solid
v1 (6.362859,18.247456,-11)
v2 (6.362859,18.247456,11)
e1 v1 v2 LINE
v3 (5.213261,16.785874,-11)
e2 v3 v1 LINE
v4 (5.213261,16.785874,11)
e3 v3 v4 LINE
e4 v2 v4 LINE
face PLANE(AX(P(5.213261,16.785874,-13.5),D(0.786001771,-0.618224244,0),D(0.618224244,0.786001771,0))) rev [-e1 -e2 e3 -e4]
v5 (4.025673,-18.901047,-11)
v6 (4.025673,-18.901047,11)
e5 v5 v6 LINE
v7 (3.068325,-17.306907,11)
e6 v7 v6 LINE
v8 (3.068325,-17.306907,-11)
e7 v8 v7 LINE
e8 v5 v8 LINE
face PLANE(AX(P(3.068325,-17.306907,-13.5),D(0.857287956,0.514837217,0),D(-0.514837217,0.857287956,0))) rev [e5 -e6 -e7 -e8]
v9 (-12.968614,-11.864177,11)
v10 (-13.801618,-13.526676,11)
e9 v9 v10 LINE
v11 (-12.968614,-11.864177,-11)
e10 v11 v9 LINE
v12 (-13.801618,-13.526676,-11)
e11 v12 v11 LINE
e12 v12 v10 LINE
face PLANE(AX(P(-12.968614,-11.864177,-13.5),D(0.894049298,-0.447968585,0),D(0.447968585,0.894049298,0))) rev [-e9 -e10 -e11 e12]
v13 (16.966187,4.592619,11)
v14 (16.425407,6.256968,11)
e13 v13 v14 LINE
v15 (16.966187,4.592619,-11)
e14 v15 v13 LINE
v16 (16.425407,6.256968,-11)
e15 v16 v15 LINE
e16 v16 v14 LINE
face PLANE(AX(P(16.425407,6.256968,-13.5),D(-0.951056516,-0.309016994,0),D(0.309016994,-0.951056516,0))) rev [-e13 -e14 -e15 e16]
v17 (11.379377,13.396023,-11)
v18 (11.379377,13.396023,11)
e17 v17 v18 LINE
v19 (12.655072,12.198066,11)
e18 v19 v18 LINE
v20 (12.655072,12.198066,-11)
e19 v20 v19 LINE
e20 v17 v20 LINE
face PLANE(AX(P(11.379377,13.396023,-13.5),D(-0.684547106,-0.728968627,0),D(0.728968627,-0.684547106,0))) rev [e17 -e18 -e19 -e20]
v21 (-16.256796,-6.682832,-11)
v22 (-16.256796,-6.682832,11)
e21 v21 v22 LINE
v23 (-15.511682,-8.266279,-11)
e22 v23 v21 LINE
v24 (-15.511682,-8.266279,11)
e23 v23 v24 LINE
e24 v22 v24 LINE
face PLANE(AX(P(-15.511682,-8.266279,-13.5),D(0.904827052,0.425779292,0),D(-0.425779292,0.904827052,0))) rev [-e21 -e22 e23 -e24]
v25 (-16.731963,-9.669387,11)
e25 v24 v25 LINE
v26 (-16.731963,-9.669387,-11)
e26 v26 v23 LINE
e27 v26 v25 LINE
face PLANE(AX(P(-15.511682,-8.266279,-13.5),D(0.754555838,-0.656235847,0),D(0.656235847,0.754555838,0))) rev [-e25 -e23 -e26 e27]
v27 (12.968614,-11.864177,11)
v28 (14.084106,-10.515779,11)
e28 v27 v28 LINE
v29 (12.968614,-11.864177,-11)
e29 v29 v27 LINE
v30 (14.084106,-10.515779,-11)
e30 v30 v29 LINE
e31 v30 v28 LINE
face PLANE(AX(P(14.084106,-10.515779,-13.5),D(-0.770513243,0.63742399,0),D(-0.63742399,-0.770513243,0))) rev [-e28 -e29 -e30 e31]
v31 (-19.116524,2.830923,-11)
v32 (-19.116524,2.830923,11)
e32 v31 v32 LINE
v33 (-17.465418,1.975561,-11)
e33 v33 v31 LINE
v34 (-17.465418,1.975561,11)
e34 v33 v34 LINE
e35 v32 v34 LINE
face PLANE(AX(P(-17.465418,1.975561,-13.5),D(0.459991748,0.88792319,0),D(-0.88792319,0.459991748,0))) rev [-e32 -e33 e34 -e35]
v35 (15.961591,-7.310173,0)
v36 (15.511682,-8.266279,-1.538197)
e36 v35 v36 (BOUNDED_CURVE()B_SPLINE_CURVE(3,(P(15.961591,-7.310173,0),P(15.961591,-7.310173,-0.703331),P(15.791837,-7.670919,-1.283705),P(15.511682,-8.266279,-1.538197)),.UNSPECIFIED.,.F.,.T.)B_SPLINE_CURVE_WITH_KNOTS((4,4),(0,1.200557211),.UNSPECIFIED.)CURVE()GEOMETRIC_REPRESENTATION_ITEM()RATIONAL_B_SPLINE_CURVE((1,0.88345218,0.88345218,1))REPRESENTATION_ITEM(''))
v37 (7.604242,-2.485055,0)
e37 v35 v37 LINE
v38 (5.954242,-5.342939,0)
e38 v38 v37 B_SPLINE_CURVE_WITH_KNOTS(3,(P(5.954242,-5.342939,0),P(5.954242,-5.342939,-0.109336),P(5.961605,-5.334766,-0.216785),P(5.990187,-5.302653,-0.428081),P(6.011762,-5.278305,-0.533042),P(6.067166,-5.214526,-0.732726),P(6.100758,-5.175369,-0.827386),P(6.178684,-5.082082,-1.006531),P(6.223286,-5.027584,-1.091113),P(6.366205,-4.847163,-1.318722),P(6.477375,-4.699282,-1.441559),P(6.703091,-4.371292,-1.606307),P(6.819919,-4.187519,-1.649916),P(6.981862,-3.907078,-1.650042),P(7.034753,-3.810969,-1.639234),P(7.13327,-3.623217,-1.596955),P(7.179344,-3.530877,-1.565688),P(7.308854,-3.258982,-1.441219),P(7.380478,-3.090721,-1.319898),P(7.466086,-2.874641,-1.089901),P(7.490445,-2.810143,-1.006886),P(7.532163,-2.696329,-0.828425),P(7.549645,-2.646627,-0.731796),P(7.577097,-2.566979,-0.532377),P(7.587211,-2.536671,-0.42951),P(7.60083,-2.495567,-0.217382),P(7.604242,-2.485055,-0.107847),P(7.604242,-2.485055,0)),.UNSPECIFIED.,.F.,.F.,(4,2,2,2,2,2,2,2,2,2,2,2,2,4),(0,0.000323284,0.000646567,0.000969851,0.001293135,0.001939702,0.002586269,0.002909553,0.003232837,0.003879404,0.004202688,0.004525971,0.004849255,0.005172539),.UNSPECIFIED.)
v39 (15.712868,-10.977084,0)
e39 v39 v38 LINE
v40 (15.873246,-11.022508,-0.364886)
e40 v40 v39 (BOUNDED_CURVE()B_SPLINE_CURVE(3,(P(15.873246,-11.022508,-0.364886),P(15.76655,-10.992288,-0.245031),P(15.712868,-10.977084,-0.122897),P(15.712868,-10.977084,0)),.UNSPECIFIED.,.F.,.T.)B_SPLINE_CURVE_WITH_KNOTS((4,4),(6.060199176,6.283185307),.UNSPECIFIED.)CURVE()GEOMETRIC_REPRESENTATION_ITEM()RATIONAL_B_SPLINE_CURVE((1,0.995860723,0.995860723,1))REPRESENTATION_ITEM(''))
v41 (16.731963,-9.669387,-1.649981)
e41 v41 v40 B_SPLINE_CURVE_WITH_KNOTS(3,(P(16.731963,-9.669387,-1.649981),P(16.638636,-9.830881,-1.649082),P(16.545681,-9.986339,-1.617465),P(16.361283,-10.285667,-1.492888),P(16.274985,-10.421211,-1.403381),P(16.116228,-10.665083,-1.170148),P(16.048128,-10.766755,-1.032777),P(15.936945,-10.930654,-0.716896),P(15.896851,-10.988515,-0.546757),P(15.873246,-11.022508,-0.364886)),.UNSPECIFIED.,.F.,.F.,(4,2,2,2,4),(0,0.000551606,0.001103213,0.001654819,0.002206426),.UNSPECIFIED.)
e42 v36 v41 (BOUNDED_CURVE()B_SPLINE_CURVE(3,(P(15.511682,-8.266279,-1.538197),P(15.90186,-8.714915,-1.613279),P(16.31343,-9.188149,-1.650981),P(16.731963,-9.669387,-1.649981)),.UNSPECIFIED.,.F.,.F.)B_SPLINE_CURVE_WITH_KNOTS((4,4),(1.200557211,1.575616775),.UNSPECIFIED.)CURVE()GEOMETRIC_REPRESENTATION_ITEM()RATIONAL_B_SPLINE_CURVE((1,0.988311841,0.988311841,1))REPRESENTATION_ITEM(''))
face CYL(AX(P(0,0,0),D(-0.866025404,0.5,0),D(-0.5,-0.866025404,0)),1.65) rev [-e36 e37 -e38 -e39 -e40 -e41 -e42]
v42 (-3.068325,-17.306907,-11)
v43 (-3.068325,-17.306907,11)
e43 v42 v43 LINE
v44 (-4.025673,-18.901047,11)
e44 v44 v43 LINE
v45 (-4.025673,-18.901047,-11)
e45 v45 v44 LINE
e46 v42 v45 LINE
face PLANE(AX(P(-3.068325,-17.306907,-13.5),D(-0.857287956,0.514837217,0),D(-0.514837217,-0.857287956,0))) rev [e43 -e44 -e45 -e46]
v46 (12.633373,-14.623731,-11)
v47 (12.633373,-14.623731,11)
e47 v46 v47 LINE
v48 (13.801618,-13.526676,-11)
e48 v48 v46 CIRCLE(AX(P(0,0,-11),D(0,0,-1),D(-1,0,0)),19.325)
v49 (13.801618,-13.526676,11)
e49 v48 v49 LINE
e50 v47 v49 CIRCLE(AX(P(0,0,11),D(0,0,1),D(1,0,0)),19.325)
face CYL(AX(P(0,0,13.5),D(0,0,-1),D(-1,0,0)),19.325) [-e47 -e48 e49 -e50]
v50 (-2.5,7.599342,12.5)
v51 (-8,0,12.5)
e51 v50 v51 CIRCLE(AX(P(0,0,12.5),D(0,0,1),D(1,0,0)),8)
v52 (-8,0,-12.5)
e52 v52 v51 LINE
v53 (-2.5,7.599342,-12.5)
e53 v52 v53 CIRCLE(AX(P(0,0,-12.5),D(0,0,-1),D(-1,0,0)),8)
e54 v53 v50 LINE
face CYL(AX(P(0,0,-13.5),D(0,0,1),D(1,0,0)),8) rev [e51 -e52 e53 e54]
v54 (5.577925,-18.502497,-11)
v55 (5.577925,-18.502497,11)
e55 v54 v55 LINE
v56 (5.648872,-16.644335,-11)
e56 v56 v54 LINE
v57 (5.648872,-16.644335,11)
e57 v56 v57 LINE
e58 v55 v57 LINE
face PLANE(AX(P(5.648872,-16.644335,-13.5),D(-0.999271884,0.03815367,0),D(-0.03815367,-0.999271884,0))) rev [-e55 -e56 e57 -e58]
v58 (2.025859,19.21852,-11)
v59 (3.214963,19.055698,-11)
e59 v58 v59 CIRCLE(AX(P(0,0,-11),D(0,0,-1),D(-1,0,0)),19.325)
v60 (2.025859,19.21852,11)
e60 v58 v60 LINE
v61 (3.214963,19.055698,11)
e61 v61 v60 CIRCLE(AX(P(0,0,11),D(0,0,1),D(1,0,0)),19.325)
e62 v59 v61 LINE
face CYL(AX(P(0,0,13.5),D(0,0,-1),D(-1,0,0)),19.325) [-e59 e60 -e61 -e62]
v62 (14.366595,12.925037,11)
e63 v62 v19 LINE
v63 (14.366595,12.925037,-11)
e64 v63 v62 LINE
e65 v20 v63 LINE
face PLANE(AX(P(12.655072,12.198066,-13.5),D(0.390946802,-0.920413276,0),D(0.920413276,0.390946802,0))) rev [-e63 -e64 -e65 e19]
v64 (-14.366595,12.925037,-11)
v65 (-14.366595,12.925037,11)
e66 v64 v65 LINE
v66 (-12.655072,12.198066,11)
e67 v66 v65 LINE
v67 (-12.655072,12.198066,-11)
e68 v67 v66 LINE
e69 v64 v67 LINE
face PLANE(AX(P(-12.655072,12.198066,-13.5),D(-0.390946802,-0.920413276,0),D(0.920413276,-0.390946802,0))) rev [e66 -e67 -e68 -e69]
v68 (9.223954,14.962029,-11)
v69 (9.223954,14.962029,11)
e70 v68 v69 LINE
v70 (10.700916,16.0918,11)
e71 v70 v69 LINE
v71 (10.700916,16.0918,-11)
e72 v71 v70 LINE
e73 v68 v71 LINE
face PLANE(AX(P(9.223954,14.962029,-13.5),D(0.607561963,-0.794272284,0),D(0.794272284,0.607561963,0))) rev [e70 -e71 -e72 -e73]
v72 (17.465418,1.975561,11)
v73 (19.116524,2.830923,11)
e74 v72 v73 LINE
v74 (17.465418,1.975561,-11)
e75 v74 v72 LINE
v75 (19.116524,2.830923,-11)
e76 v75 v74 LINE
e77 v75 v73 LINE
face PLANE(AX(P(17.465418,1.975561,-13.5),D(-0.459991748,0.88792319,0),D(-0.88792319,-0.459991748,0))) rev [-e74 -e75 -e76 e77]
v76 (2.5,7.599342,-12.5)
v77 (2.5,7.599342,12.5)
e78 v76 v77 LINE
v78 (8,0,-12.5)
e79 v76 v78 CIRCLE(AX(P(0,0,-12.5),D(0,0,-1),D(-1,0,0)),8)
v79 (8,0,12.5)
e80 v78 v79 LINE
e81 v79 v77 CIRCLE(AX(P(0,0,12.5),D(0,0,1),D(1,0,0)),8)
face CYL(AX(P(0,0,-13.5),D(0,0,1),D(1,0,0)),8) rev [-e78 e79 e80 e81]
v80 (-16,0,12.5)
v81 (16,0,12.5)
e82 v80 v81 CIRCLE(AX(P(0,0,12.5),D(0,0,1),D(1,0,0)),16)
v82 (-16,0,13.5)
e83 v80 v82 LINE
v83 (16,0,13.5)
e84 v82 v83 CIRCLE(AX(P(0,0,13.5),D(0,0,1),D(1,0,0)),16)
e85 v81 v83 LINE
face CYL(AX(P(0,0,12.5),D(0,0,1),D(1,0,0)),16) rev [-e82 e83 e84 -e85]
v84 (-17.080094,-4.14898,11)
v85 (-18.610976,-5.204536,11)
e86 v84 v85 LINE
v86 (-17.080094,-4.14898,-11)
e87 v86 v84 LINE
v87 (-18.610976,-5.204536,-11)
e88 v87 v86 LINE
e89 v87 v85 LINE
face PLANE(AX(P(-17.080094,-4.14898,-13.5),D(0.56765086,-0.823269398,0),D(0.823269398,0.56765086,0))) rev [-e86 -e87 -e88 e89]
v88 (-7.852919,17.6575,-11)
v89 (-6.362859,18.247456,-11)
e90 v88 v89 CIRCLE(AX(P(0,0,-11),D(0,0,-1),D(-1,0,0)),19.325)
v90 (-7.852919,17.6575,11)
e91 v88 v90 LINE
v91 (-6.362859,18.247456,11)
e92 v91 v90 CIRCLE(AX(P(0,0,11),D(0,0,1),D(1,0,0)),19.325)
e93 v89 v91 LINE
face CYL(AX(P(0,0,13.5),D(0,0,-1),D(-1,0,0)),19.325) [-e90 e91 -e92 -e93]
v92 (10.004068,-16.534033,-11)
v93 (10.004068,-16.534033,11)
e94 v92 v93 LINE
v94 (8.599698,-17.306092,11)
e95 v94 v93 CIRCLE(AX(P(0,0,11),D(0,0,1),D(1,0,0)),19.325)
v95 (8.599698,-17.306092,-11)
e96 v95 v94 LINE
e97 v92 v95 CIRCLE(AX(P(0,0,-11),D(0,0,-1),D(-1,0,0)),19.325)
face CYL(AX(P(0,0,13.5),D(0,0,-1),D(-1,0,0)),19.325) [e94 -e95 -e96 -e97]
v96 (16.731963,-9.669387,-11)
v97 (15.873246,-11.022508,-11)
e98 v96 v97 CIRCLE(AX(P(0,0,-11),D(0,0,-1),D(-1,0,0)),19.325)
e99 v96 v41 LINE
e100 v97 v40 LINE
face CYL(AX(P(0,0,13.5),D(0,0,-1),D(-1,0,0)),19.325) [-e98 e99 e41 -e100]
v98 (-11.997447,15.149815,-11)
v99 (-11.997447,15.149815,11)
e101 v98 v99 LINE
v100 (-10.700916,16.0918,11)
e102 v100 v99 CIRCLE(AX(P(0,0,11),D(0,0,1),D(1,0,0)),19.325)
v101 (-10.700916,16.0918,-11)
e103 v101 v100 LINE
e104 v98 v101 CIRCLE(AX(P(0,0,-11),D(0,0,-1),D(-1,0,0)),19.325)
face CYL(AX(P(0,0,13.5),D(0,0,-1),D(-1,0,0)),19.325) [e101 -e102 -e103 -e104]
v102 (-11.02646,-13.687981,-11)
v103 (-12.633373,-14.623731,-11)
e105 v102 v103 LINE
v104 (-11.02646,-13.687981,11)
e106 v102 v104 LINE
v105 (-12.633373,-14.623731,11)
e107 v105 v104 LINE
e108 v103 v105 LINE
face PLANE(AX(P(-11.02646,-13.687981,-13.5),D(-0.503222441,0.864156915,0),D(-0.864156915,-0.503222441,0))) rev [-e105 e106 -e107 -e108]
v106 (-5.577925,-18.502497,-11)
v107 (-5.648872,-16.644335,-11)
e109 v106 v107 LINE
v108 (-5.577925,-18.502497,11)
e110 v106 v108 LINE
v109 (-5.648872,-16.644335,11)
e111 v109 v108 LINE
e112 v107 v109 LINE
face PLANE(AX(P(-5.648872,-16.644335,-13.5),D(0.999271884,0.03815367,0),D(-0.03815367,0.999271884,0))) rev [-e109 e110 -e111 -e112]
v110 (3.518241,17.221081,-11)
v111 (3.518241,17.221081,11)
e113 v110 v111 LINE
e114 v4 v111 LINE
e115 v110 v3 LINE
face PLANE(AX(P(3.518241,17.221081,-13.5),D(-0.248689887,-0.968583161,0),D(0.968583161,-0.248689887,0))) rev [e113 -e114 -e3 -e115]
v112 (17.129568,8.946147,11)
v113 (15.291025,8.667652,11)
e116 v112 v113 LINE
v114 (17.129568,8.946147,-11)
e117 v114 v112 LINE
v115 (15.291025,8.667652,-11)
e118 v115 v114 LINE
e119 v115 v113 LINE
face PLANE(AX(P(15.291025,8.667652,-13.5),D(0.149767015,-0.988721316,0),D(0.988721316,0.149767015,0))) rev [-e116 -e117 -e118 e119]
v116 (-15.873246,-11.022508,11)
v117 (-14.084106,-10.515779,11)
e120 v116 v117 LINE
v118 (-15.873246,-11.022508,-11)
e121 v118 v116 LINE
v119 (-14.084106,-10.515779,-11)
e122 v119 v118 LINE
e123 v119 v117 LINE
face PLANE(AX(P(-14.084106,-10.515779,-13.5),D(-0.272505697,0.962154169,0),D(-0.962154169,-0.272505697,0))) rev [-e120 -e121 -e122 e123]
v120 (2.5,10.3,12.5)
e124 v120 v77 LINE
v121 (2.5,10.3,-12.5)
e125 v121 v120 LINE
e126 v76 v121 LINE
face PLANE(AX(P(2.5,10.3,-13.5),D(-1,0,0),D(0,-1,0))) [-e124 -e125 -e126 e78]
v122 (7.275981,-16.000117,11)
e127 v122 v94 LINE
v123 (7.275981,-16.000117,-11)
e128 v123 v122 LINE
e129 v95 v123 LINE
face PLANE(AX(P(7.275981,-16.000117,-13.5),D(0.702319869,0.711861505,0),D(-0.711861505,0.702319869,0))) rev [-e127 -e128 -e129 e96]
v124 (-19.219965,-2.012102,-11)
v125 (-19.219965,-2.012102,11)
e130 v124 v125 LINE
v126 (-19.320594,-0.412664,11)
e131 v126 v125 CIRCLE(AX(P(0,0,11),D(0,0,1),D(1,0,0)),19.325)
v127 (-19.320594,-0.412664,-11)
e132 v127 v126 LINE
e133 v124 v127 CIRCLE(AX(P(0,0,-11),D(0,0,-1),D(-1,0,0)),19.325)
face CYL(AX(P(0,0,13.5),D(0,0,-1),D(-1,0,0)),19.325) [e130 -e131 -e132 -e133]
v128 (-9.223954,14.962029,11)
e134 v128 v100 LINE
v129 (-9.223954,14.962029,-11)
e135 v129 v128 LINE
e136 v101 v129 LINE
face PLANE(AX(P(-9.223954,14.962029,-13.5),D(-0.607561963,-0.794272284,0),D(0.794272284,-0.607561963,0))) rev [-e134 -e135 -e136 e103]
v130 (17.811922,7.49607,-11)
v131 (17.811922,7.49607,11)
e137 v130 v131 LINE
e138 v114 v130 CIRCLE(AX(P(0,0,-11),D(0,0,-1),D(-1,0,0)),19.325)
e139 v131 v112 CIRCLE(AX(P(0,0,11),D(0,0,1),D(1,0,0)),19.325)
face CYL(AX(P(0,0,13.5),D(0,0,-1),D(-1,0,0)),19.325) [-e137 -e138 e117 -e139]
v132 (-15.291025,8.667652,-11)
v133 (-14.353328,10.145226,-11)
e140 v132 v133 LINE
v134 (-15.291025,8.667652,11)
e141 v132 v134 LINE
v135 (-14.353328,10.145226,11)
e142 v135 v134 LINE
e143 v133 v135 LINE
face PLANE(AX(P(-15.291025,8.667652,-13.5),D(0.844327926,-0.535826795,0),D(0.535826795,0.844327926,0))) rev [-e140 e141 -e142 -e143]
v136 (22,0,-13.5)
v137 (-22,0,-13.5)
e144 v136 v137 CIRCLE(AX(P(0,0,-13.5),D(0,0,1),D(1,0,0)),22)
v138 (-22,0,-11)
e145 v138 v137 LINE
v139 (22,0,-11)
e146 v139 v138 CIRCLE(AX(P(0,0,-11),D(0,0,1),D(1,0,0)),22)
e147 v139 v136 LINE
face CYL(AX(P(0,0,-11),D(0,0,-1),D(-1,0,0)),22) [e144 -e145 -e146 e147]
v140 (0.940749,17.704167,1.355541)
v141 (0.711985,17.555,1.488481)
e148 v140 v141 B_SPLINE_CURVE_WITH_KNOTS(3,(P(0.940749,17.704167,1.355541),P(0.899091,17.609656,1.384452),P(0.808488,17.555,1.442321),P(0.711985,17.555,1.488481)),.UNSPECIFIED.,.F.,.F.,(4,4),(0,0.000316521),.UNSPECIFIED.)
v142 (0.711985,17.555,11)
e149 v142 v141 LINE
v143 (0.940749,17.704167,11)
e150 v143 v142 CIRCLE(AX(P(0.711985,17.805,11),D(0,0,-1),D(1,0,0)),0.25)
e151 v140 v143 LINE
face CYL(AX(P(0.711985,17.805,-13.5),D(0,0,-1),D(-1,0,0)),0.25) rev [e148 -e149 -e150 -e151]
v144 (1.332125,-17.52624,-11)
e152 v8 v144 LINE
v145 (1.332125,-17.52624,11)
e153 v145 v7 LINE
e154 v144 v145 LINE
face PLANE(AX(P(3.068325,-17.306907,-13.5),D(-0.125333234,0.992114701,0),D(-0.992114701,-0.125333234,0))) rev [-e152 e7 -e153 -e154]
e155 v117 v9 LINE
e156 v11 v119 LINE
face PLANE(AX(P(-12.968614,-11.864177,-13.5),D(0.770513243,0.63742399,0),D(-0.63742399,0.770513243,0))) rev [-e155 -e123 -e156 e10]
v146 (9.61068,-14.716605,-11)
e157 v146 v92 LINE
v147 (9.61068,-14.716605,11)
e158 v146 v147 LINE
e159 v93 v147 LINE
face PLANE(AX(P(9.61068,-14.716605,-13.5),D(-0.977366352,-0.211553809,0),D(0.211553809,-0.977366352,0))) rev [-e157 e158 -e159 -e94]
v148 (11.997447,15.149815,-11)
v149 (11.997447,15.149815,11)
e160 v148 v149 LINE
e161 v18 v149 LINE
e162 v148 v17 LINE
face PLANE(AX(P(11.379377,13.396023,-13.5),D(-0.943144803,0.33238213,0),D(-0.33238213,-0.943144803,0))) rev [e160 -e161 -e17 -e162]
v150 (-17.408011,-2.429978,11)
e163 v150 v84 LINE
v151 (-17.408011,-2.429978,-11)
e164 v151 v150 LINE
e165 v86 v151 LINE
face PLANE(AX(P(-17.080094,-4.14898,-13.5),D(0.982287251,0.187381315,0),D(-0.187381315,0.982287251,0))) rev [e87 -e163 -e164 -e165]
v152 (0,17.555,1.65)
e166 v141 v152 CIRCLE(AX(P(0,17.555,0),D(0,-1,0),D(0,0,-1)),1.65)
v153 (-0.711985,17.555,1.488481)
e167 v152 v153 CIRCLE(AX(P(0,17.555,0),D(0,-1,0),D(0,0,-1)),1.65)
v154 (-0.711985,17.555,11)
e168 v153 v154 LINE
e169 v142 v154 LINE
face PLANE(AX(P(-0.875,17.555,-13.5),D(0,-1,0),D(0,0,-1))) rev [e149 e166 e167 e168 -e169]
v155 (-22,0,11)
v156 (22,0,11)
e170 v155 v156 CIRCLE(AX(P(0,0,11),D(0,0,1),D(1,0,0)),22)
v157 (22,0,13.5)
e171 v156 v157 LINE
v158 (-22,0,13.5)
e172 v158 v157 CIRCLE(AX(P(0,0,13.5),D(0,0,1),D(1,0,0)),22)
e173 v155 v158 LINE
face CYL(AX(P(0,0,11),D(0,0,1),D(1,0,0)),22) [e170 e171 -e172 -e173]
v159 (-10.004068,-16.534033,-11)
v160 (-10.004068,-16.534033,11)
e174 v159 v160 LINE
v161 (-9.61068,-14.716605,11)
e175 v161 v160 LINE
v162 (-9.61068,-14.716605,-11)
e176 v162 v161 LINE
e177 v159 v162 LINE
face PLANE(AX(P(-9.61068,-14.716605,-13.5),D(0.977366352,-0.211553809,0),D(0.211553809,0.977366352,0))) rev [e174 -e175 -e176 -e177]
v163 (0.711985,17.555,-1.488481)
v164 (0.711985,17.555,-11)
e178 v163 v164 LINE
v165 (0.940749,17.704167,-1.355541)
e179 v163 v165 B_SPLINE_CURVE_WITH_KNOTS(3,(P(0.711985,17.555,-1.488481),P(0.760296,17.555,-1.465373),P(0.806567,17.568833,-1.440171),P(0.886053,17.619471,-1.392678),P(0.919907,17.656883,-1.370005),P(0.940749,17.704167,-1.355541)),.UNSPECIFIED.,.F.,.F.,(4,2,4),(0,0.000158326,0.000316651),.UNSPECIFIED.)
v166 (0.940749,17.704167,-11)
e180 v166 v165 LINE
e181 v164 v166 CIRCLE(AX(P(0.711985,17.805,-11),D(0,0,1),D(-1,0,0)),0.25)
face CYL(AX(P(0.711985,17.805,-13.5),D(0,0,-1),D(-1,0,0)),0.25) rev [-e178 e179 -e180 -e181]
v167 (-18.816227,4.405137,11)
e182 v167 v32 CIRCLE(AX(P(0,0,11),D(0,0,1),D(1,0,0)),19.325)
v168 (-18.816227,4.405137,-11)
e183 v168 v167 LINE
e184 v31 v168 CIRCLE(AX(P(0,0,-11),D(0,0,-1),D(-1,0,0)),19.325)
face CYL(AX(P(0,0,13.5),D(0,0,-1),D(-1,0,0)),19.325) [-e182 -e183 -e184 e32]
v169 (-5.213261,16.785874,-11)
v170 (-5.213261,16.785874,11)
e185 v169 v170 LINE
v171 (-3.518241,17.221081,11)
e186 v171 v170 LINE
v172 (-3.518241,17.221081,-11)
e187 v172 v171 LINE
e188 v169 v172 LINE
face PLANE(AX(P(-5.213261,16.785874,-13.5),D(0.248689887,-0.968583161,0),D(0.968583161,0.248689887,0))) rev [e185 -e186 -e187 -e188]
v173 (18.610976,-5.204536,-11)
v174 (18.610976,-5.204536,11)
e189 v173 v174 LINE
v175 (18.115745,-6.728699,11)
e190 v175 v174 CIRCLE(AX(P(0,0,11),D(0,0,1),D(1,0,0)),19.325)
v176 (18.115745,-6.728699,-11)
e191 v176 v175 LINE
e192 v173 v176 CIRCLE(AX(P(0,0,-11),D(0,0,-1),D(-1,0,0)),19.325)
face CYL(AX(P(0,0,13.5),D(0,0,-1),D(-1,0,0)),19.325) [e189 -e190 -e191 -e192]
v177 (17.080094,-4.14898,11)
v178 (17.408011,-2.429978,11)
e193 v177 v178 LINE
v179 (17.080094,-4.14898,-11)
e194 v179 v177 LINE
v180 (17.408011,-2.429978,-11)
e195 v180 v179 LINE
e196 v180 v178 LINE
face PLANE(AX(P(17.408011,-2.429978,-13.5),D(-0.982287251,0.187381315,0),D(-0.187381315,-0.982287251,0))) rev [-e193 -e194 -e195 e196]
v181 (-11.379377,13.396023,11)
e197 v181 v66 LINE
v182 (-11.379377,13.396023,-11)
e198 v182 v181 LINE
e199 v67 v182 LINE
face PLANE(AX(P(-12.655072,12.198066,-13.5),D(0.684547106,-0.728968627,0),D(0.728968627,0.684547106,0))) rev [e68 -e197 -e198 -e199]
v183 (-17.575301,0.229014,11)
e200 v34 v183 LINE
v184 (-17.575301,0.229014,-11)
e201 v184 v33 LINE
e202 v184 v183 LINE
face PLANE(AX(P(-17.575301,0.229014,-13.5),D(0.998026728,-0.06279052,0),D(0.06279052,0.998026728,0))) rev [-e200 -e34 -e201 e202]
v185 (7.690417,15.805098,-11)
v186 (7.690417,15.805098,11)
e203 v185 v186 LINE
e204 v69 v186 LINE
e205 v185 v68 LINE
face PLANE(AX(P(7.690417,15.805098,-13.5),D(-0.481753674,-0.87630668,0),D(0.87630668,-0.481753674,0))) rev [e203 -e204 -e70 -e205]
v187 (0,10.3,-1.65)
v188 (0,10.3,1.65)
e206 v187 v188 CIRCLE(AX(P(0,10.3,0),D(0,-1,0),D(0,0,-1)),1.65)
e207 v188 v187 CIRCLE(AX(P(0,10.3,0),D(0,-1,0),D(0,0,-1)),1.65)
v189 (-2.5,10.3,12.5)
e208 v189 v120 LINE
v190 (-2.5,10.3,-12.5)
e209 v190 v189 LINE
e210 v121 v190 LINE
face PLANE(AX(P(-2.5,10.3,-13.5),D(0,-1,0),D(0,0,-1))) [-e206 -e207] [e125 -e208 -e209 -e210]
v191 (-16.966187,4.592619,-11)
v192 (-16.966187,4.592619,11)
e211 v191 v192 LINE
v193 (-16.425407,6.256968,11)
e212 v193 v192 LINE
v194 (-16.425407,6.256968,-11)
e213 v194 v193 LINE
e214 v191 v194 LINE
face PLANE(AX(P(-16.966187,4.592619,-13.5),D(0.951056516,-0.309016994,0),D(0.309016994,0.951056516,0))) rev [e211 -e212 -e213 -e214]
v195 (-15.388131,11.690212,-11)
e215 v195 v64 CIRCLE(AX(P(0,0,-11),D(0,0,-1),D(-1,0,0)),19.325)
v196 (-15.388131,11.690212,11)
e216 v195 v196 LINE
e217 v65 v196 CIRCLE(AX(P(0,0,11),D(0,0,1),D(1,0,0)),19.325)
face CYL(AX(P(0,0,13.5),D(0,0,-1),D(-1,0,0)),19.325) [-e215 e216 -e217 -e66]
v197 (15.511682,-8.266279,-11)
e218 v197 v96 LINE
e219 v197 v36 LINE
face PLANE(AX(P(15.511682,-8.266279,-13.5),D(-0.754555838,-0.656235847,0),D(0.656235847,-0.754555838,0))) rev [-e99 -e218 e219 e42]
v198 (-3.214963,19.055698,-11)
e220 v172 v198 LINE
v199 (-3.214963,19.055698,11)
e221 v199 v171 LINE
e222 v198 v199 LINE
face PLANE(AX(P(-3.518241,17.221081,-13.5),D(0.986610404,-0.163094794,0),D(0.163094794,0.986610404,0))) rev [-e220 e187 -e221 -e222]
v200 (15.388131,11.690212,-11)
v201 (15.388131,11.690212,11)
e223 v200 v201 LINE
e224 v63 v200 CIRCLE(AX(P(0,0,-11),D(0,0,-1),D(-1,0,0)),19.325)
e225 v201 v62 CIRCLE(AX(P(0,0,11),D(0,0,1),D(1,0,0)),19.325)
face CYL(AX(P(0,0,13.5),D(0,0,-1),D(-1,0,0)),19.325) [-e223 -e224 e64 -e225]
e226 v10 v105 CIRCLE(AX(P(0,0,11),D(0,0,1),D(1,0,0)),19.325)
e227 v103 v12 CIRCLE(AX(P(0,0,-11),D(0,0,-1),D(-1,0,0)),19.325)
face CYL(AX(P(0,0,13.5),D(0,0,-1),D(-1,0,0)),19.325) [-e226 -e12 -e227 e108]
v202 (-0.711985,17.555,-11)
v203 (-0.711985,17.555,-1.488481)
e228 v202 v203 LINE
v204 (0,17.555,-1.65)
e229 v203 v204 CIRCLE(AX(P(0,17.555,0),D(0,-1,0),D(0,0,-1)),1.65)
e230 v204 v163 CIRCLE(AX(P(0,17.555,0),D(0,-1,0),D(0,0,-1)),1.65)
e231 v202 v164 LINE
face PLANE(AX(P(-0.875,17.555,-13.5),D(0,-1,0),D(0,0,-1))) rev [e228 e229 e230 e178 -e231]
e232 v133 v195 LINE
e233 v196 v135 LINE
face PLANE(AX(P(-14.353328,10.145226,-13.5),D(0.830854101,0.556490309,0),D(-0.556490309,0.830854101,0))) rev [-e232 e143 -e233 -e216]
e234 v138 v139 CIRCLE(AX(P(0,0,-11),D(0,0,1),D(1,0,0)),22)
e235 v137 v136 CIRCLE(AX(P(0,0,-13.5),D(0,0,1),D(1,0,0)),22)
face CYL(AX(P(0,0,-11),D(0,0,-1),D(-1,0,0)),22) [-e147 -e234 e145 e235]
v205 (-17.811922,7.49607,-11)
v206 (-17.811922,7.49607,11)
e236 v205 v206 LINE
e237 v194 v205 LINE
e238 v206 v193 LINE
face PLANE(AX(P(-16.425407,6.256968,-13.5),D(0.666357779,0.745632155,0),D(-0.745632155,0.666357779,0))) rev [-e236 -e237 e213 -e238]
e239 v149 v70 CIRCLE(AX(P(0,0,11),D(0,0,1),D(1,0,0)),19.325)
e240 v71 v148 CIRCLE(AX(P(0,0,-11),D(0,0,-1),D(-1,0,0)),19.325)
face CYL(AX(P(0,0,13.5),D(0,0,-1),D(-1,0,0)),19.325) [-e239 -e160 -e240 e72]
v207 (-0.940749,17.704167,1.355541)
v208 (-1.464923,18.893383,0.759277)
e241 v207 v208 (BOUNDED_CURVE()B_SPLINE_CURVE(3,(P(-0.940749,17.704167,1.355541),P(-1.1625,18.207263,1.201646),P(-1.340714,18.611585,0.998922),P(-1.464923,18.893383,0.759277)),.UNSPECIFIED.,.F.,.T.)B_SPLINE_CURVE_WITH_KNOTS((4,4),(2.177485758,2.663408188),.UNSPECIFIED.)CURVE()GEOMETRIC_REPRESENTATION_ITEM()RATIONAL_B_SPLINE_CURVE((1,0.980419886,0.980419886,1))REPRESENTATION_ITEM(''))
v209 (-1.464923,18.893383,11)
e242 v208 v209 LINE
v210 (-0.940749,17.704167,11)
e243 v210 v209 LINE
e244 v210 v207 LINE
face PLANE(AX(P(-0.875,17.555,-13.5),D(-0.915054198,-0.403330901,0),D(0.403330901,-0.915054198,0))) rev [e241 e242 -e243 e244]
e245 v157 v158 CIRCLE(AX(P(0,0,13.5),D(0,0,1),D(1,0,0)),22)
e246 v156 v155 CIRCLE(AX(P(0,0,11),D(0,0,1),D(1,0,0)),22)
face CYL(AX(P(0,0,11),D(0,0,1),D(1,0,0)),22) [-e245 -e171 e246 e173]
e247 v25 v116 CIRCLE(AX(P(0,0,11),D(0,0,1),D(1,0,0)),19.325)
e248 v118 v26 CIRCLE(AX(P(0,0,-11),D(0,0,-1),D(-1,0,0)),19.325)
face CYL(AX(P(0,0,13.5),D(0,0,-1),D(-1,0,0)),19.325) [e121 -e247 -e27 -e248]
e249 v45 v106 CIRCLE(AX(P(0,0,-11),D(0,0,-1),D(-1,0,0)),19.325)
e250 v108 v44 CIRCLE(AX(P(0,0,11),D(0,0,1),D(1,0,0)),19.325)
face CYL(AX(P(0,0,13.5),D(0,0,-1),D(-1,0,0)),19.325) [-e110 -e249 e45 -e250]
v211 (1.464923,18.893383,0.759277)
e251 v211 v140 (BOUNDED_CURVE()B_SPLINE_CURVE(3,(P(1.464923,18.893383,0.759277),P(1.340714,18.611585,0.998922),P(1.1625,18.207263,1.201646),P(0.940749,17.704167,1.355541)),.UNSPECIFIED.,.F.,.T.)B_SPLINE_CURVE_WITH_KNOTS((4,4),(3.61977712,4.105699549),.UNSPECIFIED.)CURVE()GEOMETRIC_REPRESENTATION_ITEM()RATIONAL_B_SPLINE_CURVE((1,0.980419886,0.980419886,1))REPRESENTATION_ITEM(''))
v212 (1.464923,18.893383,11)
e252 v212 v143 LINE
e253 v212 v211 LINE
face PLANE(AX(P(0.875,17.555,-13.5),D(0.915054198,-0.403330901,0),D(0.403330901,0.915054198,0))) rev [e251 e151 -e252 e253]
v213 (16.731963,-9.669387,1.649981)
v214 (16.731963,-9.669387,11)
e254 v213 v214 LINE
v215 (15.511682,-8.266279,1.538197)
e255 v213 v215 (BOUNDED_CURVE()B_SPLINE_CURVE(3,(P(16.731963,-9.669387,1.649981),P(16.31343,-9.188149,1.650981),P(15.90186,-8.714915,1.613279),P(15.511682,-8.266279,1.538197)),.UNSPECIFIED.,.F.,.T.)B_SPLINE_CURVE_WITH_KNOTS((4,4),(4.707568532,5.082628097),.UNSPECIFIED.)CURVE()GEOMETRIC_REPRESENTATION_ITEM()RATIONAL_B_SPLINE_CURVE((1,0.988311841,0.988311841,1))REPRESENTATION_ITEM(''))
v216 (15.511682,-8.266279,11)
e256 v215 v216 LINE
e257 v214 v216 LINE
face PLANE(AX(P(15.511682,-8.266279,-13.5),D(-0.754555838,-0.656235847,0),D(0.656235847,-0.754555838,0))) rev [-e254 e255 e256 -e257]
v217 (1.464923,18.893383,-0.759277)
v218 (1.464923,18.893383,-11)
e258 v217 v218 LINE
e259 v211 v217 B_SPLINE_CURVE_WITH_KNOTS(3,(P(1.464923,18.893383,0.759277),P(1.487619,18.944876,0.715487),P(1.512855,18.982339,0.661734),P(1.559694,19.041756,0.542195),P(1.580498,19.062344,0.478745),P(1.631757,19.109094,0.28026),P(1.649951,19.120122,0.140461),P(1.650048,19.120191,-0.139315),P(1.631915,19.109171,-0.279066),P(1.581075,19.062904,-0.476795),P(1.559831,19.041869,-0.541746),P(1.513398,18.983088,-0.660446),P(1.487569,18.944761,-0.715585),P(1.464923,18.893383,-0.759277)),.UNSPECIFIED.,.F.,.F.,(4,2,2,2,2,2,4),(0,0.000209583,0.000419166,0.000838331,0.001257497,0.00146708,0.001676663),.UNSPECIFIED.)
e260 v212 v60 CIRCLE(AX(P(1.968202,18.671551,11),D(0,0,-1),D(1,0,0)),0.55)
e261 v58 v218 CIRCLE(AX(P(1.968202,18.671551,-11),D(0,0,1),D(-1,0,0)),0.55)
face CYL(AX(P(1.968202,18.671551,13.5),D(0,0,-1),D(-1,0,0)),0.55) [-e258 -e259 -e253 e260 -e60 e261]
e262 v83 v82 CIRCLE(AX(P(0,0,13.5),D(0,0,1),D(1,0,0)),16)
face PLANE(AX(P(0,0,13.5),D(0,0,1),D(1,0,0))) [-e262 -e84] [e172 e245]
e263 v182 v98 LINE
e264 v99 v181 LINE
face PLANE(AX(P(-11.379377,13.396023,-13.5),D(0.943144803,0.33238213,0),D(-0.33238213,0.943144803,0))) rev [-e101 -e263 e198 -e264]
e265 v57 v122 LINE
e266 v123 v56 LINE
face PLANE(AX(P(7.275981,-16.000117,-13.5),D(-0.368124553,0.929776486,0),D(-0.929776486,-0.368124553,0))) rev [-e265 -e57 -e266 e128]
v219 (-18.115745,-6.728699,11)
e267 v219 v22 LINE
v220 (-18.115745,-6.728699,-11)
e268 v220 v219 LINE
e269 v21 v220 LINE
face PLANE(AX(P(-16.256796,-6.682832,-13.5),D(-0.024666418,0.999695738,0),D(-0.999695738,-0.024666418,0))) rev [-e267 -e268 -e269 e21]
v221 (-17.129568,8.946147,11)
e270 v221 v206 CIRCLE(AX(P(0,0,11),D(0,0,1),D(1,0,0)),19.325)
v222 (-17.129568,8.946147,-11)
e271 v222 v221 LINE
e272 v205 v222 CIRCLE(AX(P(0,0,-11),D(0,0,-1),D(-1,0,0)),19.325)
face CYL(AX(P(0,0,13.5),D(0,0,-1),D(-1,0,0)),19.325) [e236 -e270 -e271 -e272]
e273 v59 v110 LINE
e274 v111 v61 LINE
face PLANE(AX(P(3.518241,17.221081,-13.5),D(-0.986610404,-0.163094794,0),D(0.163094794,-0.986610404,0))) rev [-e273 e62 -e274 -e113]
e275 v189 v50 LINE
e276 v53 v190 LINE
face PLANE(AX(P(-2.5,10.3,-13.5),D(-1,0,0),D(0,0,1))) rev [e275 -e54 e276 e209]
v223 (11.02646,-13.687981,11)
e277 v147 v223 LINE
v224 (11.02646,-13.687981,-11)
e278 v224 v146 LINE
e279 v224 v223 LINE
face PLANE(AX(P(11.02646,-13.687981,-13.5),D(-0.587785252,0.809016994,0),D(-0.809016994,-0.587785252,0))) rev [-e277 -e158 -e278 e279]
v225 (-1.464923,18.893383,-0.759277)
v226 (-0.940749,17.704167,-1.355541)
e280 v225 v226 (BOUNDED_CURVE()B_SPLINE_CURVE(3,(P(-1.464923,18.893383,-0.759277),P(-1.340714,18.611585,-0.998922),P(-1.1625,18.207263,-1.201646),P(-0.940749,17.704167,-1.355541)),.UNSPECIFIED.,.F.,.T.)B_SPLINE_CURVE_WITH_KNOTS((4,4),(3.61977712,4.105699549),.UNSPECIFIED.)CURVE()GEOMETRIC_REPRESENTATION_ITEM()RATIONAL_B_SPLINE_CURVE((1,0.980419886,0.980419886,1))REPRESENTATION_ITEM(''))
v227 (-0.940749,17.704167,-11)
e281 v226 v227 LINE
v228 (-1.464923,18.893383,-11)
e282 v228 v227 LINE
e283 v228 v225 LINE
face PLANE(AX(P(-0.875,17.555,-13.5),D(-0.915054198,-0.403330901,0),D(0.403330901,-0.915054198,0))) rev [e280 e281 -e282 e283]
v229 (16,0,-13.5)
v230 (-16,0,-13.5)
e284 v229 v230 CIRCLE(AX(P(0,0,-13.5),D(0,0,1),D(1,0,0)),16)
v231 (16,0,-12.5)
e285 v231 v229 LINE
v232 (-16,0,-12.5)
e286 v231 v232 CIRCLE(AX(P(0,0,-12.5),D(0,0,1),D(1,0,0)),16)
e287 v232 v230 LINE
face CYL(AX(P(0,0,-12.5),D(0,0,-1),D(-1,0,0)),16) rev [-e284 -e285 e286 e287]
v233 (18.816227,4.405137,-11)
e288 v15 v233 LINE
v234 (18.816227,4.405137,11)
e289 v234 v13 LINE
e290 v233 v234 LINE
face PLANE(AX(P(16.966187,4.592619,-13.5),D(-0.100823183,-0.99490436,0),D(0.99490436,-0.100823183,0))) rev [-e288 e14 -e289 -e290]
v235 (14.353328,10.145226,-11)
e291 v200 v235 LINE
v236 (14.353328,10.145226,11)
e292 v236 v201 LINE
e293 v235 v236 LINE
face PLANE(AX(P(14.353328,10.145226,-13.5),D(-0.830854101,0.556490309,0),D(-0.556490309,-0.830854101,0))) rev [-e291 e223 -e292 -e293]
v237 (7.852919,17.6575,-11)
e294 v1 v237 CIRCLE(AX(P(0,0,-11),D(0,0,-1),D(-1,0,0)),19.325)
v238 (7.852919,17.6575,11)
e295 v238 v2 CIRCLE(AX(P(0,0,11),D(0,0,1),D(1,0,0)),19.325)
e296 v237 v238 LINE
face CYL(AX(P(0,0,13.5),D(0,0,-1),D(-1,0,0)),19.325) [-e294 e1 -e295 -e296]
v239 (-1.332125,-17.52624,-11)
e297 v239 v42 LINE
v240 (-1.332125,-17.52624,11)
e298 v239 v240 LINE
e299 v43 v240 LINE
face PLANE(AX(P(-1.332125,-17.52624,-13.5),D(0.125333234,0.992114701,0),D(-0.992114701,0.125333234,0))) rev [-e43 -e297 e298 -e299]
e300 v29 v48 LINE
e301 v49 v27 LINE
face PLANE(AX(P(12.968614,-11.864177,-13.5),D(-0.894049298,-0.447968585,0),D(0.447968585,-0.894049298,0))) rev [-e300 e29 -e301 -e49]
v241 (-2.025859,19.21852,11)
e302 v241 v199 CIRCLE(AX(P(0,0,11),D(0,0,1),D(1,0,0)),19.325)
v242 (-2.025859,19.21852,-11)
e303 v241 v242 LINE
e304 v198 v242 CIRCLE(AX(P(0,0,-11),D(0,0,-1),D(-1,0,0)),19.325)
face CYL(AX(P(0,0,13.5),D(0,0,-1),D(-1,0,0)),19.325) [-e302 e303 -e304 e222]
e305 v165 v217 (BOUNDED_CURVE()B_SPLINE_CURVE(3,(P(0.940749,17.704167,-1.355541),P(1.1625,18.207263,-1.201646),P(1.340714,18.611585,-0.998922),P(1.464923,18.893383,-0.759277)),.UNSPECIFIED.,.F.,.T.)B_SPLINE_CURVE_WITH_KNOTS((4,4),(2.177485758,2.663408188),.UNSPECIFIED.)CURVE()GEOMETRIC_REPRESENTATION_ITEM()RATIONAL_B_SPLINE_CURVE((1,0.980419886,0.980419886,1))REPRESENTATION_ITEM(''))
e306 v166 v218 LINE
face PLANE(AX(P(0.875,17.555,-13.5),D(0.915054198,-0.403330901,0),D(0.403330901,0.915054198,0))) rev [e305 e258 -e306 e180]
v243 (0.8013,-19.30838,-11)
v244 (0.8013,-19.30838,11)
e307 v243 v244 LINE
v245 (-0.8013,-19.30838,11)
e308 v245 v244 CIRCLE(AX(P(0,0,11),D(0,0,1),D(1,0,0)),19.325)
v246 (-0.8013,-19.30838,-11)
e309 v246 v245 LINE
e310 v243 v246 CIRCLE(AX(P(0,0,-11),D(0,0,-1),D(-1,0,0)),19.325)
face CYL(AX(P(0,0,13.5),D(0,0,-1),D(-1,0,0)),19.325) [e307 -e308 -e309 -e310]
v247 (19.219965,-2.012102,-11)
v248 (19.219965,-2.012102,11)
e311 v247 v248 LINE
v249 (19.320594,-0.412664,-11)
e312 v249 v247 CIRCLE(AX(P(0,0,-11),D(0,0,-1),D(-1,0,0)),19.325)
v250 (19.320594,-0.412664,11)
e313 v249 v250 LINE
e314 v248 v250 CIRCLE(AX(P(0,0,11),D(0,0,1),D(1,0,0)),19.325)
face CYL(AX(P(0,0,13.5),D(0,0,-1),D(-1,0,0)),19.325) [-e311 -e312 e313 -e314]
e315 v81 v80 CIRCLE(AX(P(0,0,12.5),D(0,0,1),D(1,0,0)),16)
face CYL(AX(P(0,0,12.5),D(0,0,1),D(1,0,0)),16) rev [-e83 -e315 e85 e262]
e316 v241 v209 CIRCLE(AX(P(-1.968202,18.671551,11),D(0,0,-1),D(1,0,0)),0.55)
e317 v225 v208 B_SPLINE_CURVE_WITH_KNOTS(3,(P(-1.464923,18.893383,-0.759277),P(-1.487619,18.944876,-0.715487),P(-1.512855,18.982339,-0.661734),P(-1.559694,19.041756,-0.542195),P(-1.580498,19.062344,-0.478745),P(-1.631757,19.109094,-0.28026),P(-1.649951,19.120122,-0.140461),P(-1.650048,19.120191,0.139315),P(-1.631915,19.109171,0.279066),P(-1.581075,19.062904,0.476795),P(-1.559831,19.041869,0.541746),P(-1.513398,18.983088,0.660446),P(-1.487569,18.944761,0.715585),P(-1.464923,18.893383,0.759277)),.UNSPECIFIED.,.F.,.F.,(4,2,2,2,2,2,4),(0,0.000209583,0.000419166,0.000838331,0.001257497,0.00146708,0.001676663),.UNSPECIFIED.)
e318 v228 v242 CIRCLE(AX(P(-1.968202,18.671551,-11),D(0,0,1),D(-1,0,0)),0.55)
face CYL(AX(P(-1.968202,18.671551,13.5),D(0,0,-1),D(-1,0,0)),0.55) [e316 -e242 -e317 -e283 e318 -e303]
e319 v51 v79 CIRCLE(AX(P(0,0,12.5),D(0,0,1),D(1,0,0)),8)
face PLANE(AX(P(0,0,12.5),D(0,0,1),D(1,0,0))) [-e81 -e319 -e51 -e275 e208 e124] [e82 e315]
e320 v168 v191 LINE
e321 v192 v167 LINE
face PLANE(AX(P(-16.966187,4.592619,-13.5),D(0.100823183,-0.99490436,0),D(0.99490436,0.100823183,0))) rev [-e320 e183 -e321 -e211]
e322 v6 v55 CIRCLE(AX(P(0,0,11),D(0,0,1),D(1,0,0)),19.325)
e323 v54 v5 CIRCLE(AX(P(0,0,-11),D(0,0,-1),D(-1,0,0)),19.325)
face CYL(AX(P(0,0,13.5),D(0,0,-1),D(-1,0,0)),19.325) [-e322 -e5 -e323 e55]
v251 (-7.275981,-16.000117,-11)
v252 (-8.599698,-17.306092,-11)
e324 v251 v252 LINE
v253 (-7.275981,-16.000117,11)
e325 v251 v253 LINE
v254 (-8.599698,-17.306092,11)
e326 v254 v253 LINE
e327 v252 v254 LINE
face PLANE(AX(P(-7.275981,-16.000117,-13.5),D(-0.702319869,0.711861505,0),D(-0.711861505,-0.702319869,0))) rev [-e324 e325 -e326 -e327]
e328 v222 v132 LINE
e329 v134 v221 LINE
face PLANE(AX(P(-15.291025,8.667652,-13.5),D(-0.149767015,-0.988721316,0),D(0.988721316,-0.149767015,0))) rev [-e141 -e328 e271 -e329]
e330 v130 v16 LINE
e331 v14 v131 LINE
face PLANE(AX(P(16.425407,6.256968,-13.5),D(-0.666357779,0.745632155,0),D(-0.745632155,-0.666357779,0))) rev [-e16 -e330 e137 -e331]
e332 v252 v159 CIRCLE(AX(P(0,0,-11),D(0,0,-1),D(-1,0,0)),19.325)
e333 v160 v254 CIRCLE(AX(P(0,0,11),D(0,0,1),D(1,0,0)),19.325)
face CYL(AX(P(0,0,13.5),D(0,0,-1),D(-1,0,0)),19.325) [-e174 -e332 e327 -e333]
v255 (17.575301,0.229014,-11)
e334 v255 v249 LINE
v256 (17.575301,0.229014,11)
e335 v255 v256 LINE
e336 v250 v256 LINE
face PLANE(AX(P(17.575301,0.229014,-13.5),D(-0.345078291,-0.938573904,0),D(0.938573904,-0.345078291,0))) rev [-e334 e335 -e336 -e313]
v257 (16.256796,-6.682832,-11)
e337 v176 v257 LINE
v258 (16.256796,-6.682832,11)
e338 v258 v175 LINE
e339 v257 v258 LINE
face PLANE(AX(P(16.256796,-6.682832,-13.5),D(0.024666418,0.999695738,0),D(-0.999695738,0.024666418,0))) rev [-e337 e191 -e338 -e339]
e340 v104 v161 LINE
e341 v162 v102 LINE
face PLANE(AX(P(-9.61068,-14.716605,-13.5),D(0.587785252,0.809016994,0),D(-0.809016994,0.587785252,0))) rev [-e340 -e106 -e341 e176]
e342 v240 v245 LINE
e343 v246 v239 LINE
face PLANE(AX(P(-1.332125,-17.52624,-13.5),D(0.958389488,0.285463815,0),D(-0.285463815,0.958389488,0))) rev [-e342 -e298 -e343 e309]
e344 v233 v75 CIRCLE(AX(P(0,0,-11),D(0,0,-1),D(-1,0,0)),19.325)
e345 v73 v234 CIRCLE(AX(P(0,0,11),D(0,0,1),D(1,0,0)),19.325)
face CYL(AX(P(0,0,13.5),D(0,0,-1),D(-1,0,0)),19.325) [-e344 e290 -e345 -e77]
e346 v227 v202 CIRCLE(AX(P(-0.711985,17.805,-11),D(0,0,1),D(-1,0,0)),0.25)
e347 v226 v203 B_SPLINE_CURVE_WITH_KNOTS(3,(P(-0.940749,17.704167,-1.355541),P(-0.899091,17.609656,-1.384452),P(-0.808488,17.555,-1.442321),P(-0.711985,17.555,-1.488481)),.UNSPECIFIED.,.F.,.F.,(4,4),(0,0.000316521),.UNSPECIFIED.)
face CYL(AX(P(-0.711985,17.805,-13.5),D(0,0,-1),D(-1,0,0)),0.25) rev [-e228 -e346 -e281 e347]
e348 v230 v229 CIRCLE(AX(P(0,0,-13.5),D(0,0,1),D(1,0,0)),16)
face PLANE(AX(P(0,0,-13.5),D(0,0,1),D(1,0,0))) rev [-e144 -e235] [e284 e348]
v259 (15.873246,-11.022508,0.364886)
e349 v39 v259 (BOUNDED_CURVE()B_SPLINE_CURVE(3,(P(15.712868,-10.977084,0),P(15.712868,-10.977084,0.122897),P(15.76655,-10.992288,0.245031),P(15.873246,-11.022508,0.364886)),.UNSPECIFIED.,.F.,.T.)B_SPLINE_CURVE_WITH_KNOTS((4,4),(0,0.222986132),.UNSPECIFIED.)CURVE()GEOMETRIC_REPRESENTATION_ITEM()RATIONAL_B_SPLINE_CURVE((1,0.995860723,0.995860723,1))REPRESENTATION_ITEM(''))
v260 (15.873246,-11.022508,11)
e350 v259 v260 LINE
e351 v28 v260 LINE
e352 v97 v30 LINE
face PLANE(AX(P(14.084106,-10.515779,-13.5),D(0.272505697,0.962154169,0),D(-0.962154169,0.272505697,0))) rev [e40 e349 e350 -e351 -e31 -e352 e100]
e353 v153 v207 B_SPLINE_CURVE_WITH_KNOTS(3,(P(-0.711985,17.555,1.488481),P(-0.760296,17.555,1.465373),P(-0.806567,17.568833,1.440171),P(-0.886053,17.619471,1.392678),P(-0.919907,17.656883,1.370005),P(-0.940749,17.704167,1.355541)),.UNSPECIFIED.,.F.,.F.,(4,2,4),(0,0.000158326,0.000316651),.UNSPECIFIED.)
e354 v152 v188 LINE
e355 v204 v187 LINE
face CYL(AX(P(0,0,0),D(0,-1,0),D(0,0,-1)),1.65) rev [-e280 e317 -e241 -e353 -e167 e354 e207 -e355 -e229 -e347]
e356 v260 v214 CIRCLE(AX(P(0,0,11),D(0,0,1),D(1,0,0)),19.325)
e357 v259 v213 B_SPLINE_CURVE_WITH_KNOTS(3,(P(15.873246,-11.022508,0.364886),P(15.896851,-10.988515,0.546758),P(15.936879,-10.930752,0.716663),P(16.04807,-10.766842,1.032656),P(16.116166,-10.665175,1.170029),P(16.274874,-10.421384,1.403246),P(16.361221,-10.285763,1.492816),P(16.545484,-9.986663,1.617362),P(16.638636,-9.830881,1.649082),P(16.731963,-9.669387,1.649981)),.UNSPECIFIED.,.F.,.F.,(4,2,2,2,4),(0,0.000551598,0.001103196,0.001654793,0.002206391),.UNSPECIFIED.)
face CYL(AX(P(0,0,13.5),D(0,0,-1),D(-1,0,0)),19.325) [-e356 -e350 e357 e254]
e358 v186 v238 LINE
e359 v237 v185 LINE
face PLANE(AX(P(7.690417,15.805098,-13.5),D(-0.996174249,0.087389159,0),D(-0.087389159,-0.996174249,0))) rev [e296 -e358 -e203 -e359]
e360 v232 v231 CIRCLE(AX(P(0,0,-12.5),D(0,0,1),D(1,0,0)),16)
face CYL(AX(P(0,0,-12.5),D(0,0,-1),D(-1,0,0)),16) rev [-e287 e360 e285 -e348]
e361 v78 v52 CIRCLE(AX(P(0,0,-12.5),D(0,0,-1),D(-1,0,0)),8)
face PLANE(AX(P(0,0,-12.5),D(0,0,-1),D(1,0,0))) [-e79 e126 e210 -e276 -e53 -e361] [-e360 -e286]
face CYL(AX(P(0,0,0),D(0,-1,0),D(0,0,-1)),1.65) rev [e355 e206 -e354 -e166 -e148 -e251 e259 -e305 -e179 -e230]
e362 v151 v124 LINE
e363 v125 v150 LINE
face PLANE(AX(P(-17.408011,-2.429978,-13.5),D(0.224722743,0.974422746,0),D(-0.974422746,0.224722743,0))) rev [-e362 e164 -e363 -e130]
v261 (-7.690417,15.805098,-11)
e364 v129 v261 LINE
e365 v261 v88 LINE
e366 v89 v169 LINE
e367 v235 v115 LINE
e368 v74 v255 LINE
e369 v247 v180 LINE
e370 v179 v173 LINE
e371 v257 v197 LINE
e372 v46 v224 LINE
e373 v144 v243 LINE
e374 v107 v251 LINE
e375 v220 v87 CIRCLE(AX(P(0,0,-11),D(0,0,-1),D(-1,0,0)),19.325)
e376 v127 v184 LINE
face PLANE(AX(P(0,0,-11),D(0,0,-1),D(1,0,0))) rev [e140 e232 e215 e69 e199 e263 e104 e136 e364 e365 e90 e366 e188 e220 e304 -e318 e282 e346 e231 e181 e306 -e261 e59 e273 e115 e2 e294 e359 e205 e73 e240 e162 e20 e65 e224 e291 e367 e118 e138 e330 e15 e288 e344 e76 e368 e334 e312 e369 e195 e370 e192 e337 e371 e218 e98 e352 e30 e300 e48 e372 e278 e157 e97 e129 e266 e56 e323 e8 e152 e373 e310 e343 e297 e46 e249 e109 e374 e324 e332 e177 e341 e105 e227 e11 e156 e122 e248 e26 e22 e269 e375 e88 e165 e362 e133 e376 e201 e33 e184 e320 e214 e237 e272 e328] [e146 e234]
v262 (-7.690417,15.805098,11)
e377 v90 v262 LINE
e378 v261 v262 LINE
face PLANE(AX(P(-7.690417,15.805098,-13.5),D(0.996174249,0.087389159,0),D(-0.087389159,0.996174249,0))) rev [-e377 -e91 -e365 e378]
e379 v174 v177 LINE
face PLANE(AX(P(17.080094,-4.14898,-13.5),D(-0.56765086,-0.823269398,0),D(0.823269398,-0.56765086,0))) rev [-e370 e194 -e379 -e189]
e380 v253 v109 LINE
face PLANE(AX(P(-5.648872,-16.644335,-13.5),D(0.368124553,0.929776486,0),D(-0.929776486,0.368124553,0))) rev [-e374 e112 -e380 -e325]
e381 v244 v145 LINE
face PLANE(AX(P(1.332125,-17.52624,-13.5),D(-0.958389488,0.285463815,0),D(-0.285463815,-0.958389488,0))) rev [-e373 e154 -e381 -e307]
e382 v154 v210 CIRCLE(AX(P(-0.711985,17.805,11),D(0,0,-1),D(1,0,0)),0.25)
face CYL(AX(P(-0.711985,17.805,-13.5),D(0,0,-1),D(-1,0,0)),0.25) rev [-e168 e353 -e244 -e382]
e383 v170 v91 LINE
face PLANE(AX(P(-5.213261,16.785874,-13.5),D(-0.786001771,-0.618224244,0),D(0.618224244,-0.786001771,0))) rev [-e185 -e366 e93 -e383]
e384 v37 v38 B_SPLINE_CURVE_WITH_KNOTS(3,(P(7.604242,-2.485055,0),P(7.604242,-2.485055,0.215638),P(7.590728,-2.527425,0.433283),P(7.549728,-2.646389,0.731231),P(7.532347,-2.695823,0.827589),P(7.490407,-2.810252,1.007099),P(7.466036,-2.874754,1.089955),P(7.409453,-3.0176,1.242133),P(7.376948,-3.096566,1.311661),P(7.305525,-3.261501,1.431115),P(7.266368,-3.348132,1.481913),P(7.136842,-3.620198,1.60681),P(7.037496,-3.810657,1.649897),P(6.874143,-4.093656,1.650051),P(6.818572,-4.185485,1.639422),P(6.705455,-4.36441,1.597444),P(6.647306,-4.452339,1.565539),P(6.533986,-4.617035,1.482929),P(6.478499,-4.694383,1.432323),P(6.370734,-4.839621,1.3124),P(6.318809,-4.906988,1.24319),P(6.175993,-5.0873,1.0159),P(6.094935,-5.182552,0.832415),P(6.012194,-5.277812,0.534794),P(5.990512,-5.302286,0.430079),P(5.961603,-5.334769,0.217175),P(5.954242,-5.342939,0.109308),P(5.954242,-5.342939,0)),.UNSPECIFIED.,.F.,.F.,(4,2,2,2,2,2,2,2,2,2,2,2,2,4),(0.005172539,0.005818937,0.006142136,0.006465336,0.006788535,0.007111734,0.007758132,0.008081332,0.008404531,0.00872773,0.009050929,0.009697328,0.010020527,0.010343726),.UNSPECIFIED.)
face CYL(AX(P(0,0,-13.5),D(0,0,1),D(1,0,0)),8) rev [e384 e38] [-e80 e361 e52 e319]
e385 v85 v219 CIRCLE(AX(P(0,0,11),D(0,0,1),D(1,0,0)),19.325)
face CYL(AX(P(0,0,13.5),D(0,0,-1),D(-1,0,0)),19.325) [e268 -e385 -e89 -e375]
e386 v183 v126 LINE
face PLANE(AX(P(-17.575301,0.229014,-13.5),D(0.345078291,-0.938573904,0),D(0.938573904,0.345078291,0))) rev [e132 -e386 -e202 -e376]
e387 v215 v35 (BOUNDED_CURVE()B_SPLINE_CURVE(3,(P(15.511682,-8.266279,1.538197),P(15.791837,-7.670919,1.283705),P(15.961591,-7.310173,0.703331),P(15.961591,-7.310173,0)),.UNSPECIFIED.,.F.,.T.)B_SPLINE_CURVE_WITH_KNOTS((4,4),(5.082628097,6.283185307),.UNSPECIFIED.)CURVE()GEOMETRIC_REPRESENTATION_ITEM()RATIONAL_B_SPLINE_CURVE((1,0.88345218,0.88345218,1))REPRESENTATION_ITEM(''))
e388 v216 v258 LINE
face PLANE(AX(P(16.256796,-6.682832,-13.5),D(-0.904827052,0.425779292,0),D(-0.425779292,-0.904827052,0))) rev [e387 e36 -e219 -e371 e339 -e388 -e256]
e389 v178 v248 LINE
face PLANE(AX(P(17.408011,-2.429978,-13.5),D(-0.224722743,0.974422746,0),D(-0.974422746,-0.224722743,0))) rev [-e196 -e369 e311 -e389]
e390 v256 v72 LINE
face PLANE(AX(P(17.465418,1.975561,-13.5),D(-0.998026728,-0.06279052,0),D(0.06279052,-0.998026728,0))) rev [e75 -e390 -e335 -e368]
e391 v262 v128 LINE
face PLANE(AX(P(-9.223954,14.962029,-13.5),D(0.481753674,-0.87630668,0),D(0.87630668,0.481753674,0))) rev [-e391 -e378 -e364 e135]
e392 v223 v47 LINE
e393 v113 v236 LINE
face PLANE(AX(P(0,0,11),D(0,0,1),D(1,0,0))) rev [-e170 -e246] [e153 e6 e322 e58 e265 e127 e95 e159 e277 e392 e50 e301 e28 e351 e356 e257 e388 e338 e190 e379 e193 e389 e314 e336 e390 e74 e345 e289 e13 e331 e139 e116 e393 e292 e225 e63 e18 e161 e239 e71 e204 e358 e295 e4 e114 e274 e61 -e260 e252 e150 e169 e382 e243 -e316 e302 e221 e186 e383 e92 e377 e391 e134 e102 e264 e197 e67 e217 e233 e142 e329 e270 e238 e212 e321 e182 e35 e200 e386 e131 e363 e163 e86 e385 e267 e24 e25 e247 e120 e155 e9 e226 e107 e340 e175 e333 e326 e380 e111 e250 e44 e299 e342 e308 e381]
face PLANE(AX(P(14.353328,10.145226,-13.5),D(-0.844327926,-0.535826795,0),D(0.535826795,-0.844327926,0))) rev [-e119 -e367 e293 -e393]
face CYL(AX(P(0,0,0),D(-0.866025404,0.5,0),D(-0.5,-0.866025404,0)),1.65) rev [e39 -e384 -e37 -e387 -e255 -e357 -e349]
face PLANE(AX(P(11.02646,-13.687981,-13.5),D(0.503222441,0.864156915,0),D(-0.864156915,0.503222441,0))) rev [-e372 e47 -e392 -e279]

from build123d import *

# Parameters (mm, degrees)
SKETCH_1_R               = 19.325
EXTRUDE_1_DEPTH          = 13.5
CUT_EXTRUDE_1_DEPTH      = 13.5
FILLET_3_R               = 0.55
FILLET_4_R               = 0.25
PATTERN_CIRCULAR_2_COUNT = 25
SKETCH_3_R               = 22
EXTRUDE_2_DEPTH          = 2.5
SKETCH_4_R               = 16
CUT_EXTRUDE_2_DEPTH      = 1
CUT_EXTRUDE_3_DEPTH      = 13.5
SKETCH_6_W               = 1.65
SKETCH_6_H               = 30.052558883
PATTERN_CIRCULAR_3_COUNT = 2
PATTERN_CIRCULAR_3_ANGLE = 120


with BuildPart() as part:
    # 草图1 → 凸台-拉伸1 (new, symmetric)
    with BuildSketch(Plane.XY):
        Circle(SKETCH_1_R)
    extrude(amount=EXTRUDE_1_DEPTH, both=True)

    # 草图2 → 切除-拉伸1 (cut, symmetric)
    with BuildSketch(Plane.XY):
        with BuildLine():
            Line((-0.875, 17.555), (0.875, 17.555))
            Line((0.875, 17.555), (1.625, 19.256557325))
            ThreePointArc((1.625, 19.256557325), (0, 19.325), (-1.625, 19.256557325))
            Line((-1.625, 19.256557325), (-0.875, 17.555))
        make_face()
    cut_extrude_1 = extrude(amount=CUT_EXTRUDE_1_DEPTH, both=True, mode=Mode.SUBTRACT)

    # 圆角3
    fillet_3_edges = [part.edges().sort_by_distance(p)[0] for p in [
        (-1.625, 19.256557325, 0),
        (1.625, 19.256557325, 0),
    ]]
    fillet(fillet_3_edges, radius=FILLET_3_R)

    # 圆角4
    fillet_4_edges = [part.edges().sort_by_distance(p)[0] for p in [
        (-0.875, 17.555, 0),
        (0.875, 17.555, 0),
    ]]
    fillet(fillet_4_edges, radius=FILLET_4_R)

    # 阵列(圆周)2: 切除-拉伸1 ×25 about axis
    pattern_circular_2_axis = Axis((0, 0, 0), (0, 0, 1))
    for i in range(1, PATTERN_CIRCULAR_2_COUNT):
        add(cut_extrude_1.rotate(pattern_circular_2_axis, i * 360 / PATTERN_CIRCULAR_2_COUNT), mode=Mode.SUBTRACT)

    # 草图3 → 凸台-拉伸2 (add)
    with BuildSketch(Plane.XY.offset(13.5)):
        Circle(SKETCH_3_R)
    extrude_2 = extrude(amount=-EXTRUDE_2_DEPTH)

    # 镜向1: 凸台-拉伸2 across plane
    add(extrude_2.mirror(Plane.XY))

    # 草图4 → 切除-拉伸2 (cut)
    with BuildSketch(Plane.XY.offset(13.5)):
        Circle(SKETCH_4_R)
    cut_extrude_2 = extrude(amount=-CUT_EXTRUDE_2_DEPTH, mode=Mode.SUBTRACT)

    # 镜向2: 切除-拉伸2 across plane
    add(cut_extrude_2.mirror(Plane.XY), mode=Mode.SUBTRACT)

    # 草图5 → 切除-拉伸3 (cut, symmetric)
    with BuildSketch(Plane.XY):
        with BuildLine():
            Line((-2.5, 10.3), (2.5, 10.3))
            Line((2.5, 10.3), (2.5, 7.599342077))
            ThreePointArc((2.5, 7.599342077), (0, -8), (-2.5, 7.599342077))
            Line((-2.5, 7.599342077), (-2.5, 10.3))
        make_face()
    extrude(amount=CUT_EXTRUDE_3_DEPTH, both=True, mode=Mode.SUBTRACT)

    # 草图6 → M4 螺纹孔1 (revolve, cut)
    with BuildSketch(Plane(origin=(0, 0, 0), x_dir=(0, 0, -1), z_dir=(1, 0, 0))):
        with Locations((0.825, 15.026279442)):
            Rectangle(SKETCH_6_W, SKETCH_6_H)
    hole_wizard_m4_1 = revolve(axis=Axis((0, -6.35, 0), (0, 1, 0)), mode=Mode.SUBTRACT)

    # 阵列(圆周)3: M4 螺纹孔1 ×2 about axis
    pattern_circular_3_axis = Axis((0, 0, 13.5), (0, 0, -1))
    for i in range(1, PATTERN_CIRCULAR_3_COUNT):
        add(hole_wizard_m4_1.rotate(pattern_circular_3_axis, i * PATTERN_CIRCULAR_3_ANGLE / (PATTERN_CIRCULAR_3_COUNT - 1)), mode=Mode.SUBTRACT)


solid = part.part
